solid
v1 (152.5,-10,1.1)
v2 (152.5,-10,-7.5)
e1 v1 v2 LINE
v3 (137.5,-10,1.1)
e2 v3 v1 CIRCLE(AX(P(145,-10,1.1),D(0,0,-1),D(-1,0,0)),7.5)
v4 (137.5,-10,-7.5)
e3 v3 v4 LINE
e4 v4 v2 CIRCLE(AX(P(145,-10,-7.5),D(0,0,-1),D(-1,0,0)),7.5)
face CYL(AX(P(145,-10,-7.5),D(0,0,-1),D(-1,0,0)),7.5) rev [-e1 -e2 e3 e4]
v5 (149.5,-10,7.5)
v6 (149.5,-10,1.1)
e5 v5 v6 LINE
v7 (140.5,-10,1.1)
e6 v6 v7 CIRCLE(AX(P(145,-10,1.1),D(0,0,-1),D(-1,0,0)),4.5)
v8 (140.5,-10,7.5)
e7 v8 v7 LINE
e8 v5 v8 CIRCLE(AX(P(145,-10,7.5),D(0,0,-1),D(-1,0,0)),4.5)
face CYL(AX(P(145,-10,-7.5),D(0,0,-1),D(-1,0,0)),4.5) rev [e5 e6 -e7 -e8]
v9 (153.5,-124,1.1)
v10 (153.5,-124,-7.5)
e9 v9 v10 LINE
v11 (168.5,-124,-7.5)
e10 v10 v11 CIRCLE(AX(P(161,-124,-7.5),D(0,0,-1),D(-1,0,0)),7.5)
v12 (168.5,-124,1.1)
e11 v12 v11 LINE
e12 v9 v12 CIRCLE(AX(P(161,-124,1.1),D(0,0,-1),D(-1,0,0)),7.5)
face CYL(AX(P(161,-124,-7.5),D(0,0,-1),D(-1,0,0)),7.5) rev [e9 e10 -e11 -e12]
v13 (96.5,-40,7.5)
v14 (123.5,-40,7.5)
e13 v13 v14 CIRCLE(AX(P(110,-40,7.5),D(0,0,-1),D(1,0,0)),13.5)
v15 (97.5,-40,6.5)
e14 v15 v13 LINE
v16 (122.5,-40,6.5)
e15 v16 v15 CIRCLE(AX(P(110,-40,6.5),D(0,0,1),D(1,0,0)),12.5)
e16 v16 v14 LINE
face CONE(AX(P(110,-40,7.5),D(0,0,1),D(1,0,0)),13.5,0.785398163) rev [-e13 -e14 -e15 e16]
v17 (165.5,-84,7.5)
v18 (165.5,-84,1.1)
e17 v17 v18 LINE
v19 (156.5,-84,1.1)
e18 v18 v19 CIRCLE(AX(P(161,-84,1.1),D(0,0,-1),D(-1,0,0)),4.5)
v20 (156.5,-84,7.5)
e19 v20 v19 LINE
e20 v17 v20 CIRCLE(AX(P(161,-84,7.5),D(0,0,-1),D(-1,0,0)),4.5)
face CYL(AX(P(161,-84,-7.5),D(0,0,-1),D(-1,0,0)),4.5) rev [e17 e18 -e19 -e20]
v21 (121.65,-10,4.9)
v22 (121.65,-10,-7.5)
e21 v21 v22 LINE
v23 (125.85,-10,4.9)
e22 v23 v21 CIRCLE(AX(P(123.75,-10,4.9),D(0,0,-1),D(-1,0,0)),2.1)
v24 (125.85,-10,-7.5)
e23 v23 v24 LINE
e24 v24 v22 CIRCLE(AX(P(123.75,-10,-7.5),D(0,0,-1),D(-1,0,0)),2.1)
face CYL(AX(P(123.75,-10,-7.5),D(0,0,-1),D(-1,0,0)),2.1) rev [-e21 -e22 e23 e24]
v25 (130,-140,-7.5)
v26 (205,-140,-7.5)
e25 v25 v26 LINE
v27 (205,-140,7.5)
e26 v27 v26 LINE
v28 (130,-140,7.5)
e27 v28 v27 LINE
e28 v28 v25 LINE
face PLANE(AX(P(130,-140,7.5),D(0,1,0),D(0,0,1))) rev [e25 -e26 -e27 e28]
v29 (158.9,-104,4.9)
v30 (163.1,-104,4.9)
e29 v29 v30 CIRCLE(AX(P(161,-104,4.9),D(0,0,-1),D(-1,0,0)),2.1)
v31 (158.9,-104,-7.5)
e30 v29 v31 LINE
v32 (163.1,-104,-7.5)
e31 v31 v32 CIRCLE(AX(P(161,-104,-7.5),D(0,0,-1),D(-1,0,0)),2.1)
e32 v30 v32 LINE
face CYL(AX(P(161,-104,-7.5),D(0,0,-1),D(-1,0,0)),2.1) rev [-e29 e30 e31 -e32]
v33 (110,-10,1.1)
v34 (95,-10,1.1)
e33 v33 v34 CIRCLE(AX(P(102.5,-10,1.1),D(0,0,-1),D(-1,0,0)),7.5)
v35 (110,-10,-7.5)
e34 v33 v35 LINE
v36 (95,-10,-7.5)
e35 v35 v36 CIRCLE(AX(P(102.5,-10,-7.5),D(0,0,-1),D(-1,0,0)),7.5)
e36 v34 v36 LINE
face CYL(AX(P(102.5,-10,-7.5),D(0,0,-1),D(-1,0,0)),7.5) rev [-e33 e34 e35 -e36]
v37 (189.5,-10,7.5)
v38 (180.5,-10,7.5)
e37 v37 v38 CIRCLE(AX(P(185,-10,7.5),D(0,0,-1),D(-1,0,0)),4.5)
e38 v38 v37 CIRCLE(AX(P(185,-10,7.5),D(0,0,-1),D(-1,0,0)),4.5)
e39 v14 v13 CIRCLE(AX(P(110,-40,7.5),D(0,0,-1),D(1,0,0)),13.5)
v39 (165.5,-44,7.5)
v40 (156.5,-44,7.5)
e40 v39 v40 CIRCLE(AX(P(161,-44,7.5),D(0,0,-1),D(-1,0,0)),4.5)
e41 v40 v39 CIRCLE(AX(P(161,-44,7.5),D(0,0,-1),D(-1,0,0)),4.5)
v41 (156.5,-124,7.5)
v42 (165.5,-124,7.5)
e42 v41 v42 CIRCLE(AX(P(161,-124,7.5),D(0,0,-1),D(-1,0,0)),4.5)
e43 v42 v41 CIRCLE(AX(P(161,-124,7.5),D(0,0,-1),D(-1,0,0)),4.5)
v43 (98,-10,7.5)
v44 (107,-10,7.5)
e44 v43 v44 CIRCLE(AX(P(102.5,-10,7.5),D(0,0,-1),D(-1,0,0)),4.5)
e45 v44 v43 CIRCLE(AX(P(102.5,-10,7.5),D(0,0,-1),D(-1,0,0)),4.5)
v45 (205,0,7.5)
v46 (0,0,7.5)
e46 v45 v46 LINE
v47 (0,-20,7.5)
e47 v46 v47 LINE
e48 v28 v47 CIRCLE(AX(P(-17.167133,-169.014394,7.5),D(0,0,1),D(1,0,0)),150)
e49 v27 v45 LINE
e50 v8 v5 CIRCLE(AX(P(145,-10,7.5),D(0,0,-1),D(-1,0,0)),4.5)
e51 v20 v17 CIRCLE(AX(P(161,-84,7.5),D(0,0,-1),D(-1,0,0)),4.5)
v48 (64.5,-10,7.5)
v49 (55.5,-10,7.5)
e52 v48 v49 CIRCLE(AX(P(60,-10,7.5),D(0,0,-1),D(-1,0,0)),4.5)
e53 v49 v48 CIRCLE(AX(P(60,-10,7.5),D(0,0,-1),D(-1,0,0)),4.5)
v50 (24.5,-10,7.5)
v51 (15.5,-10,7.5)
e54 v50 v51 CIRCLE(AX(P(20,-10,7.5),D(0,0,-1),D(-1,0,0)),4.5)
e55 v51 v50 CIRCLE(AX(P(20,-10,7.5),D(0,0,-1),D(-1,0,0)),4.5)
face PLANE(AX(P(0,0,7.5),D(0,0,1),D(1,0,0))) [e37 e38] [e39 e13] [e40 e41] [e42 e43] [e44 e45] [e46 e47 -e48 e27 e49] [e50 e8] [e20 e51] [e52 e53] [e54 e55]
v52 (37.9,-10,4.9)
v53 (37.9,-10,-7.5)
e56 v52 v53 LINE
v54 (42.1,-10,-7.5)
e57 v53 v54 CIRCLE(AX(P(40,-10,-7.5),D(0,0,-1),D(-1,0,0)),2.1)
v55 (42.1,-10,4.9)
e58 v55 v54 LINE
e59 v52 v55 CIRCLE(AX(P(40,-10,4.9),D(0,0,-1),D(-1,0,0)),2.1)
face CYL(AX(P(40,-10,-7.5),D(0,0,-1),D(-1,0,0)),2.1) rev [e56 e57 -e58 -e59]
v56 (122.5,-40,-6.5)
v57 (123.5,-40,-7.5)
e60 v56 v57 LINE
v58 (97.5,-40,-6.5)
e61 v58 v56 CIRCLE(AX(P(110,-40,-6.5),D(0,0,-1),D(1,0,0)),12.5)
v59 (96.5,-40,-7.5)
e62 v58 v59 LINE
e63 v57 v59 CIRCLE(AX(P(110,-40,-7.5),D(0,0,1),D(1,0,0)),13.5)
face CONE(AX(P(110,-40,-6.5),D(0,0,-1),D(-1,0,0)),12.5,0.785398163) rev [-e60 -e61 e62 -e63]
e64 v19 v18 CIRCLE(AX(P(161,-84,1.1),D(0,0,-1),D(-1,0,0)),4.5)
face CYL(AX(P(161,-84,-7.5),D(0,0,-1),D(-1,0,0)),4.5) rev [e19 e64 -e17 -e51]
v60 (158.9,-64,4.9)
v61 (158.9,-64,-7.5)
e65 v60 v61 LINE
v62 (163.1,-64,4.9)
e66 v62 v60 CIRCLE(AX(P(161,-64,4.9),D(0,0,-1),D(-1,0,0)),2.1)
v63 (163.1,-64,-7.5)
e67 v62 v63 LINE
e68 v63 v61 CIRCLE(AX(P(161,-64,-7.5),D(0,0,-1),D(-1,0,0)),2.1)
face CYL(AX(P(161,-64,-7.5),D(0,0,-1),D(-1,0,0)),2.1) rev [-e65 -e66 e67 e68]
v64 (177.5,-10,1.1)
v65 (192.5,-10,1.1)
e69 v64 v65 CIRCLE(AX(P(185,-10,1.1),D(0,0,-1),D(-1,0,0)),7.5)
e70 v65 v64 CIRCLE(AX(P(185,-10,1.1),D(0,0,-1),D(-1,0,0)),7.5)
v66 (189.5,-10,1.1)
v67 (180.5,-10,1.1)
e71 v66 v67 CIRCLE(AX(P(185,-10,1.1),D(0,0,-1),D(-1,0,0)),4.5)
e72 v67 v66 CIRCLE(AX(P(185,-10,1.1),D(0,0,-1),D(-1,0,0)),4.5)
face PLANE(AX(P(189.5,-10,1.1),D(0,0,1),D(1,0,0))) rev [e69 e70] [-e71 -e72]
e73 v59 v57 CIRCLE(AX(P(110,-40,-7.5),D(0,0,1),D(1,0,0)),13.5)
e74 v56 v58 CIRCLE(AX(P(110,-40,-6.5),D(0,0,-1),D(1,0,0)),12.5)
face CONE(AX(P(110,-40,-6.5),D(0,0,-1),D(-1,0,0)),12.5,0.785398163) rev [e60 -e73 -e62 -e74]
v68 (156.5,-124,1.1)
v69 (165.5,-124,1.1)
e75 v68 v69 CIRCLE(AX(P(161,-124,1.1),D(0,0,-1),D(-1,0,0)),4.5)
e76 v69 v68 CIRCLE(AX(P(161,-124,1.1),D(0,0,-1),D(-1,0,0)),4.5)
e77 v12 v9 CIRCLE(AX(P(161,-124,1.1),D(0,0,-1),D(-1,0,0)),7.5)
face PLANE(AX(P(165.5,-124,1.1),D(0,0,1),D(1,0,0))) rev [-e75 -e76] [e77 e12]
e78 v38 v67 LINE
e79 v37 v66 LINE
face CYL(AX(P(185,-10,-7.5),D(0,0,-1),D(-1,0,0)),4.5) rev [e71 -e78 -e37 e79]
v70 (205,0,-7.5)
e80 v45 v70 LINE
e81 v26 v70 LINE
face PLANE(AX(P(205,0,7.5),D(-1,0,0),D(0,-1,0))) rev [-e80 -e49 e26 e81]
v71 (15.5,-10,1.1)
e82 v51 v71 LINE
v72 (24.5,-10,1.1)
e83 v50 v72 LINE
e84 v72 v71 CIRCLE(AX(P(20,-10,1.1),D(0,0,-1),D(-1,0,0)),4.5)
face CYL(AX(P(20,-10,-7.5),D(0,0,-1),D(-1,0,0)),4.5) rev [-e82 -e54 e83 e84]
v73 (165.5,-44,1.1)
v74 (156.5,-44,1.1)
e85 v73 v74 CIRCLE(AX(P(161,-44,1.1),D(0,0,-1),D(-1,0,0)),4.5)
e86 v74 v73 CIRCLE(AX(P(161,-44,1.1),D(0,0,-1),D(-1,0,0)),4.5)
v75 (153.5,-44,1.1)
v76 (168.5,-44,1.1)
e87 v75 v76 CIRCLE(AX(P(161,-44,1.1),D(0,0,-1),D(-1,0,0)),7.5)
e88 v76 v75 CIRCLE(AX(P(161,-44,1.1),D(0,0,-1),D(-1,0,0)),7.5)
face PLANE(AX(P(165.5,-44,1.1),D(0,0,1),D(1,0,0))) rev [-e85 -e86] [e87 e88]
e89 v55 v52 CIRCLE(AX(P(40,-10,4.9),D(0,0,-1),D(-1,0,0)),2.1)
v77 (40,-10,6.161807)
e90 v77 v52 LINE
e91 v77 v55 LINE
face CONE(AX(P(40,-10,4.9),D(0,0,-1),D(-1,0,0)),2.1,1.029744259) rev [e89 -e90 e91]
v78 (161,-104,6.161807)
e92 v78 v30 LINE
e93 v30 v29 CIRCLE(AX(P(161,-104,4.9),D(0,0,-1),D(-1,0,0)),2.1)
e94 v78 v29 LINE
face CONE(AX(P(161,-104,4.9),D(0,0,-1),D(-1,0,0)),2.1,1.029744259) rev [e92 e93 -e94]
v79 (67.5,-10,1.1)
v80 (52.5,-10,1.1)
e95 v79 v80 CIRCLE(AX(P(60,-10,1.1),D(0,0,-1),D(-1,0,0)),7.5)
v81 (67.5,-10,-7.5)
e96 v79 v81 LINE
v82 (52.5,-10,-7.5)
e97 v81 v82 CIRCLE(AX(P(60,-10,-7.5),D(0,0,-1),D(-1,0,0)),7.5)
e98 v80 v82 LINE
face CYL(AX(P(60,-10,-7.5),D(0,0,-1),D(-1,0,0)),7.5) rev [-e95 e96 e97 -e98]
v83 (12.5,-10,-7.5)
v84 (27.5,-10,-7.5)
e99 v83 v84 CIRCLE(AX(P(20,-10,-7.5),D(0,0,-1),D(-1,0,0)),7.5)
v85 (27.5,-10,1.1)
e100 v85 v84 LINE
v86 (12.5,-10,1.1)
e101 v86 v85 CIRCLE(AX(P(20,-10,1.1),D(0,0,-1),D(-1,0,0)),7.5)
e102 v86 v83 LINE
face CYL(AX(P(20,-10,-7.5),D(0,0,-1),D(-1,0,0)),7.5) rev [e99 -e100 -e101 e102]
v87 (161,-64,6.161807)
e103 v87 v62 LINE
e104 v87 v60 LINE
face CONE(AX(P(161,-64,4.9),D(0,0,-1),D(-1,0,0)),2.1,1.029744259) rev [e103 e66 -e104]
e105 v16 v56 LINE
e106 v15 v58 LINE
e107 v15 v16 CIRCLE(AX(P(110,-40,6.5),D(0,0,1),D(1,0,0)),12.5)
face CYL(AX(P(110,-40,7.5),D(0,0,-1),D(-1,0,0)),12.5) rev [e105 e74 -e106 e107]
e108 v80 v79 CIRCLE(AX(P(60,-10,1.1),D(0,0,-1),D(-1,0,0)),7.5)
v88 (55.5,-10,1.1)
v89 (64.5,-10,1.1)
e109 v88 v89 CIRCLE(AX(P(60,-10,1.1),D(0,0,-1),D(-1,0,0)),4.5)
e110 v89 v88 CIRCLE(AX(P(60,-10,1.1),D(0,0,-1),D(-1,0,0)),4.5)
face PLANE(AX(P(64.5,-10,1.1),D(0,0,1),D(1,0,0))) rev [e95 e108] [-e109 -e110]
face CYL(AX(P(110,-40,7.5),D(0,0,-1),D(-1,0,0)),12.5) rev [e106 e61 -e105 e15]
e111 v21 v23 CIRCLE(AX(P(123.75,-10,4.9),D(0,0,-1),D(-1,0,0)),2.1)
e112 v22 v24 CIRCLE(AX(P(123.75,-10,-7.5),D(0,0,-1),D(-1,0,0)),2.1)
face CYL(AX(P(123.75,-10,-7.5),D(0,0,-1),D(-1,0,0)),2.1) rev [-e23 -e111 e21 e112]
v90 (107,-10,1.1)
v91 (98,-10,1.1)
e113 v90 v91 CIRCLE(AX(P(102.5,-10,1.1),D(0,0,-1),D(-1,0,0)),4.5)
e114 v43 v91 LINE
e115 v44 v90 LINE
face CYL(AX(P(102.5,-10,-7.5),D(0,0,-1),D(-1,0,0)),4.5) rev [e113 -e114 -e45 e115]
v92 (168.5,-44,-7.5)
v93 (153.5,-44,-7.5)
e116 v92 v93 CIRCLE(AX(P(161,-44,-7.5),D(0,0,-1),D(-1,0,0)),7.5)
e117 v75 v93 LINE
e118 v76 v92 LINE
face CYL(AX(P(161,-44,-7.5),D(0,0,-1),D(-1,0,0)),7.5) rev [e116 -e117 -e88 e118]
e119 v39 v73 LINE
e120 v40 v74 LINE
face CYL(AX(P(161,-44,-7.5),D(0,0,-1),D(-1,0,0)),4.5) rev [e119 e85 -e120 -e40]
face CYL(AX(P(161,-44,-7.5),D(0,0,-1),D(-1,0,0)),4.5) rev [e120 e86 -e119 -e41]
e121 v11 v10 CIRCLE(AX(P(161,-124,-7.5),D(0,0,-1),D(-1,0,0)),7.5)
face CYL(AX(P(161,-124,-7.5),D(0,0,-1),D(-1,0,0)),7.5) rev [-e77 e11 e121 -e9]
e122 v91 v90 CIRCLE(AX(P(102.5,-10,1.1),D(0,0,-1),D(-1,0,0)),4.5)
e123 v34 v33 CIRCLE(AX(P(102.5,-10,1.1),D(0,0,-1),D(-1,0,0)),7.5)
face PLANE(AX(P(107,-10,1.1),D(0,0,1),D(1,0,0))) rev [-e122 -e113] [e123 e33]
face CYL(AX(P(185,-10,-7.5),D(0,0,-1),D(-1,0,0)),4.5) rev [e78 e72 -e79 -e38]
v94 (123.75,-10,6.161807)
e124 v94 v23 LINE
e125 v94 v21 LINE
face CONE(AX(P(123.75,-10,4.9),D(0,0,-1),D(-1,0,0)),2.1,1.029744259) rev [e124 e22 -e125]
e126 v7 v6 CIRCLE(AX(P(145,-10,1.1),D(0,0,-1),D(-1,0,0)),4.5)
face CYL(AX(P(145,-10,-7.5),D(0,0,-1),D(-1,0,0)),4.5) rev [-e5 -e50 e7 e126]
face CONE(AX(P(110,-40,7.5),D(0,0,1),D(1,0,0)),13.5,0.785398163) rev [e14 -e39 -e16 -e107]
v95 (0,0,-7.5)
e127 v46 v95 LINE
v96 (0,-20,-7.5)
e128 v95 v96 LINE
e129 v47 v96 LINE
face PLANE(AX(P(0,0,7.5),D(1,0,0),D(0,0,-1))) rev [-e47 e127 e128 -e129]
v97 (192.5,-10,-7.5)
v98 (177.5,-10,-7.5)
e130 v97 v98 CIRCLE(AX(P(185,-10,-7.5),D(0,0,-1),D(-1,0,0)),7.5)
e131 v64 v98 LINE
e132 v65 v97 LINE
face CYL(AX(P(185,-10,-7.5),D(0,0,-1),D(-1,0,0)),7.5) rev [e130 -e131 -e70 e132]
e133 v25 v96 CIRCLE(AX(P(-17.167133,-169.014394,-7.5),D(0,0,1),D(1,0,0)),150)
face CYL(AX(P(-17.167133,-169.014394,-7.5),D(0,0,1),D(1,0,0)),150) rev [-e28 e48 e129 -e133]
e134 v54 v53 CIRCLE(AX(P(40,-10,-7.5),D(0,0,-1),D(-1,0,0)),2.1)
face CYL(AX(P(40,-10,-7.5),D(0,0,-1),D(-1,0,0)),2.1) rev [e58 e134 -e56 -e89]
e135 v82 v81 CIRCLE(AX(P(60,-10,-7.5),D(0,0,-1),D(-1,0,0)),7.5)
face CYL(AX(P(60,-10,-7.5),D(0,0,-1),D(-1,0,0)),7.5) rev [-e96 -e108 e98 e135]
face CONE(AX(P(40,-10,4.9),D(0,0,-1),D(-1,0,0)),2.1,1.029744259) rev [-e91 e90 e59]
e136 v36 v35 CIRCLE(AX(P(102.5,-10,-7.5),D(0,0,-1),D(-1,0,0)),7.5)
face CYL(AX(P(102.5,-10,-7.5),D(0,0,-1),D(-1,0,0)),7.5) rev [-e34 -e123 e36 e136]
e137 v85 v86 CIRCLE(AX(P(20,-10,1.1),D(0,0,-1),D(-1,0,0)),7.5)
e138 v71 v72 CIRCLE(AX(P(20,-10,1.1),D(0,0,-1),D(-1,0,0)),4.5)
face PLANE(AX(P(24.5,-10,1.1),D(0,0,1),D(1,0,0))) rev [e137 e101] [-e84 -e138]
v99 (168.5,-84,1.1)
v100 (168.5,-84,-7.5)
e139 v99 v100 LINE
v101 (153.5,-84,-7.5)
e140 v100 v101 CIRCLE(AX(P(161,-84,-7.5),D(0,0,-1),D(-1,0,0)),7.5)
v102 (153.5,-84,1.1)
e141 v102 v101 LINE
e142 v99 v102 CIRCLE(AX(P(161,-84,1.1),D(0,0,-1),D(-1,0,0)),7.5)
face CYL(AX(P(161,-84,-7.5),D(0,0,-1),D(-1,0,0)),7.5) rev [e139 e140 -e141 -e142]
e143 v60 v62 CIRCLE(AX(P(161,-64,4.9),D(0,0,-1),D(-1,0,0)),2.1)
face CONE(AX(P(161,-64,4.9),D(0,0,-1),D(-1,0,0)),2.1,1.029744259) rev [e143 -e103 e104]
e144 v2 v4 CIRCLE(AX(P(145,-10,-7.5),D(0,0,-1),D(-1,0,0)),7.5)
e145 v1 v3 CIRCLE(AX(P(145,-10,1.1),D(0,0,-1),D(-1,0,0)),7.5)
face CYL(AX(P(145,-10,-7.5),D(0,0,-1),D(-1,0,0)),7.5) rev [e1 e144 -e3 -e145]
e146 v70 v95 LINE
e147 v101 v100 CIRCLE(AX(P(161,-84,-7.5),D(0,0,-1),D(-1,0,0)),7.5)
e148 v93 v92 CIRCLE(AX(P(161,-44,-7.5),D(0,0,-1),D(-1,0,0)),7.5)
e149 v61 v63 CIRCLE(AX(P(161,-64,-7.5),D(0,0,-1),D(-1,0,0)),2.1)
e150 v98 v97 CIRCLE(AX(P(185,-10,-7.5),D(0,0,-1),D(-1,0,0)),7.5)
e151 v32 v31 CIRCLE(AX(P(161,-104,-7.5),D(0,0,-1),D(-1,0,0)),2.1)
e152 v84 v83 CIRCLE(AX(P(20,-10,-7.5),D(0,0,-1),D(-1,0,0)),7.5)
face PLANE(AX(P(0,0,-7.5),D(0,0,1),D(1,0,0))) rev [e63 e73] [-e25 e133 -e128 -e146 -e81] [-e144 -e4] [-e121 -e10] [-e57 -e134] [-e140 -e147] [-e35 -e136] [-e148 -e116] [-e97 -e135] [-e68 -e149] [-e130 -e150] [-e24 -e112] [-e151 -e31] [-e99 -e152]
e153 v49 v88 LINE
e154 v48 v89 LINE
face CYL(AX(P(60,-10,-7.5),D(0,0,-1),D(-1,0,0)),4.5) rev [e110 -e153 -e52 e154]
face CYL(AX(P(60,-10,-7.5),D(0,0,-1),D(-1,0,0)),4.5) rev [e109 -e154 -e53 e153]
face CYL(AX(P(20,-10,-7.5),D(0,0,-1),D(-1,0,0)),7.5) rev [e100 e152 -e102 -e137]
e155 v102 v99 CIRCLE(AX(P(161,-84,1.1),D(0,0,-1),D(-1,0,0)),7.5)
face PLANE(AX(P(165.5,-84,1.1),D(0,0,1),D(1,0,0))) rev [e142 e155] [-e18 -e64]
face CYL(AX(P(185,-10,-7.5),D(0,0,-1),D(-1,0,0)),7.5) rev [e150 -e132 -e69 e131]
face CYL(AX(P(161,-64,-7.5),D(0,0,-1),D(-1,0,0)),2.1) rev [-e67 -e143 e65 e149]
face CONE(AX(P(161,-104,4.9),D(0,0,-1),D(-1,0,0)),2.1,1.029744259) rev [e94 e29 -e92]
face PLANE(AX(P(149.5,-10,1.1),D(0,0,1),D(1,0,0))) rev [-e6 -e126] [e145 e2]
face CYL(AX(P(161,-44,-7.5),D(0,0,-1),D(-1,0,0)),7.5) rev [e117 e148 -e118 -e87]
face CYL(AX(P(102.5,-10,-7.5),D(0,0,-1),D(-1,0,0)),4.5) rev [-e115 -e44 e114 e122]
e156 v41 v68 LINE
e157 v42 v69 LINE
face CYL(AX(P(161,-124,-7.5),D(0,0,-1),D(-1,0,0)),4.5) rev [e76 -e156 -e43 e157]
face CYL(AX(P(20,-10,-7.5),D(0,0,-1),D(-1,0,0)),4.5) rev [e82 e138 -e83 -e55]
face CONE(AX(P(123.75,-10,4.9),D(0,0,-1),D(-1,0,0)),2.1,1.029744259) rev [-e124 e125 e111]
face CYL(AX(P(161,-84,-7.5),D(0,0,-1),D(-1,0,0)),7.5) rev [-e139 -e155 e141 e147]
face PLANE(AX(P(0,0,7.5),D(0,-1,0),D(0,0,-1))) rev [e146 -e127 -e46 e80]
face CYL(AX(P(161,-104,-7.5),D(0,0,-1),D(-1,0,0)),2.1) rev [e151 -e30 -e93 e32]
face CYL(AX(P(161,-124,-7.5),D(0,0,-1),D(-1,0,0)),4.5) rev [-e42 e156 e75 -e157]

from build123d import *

# Parameters (mm, degrees)
EXTRUDE_1_DEPTH              = 7.5
HOLE_WIZARD_M8_2_D           = 9
HOLE_WIZARD_M8_2_CBORE_D     = 15
HOLE_WIZARD_M8_2_CBORE_DEPTH = 8.6
HOLE_WIZARD_M5_1_D           = 4.2
HOLE_WIZARD_M5_1_DEPTH       = 12.4
HOLE_WIZARD_M5_1_TIP         = 1.2618073
SKETCH_11_R                  = 150
CUT_EXTRUDE_4_DEPTH          = 249.696602309
SKETCH_12_R                  = 12.5
CUT_EXTRUDE_5_DEPTH          = 249.696602309
CHAMFER_1_SIZE               = 1


with BuildPart() as part:
    # 草图1 → 凸台-拉伸1 (new, symmetric)
    with BuildSketch(Plane.XY):
        Polygon((0, 0), (205, 0), (205, -140), (130, -140), (0, -20), align=None)
    extrude(amount=EXTRUDE_1_DEPTH, both=True)

    # M8 六角凹头螺钉的柱形沉头孔2 (through all)
    with Locations(Plane(origin=(0, 0, -7.5), x_dir=(1, 0, 0), z_dir=(0, 0, -1))):
        with Locations((20, 10), (60, 10), (102.5, 10), (145, 10), (161, 44), (161, 84), (161, 124), (185, 10)):
            CounterBoreHole(HOLE_WIZARD_M8_2_D / 2, HOLE_WIZARD_M8_2_CBORE_D / 2, HOLE_WIZARD_M8_2_CBORE_DEPTH)

    # M5 螺纹孔1
    with Locations(Plane(origin=(0, 0, -7.5), x_dir=(1, 0, 0), z_dir=(0, 0, -1))):
        with Locations((40, 10), (123.75, 10), (161, 64), (161, 104)):
            Hole(HOLE_WIZARD_M5_1_D / 2, depth=HOLE_WIZARD_M5_1_DEPTH)
            with Locations((0, 0, -(HOLE_WIZARD_M5_1_DEPTH + HOLE_WIZARD_M5_1_TIP / 2))):  # 118° drill point
                Cone(0, HOLE_WIZARD_M5_1_D / 2, HOLE_WIZARD_M5_1_TIP, mode=Mode.SUBTRACT)

    # 草图11 → 切除-拉伸4 (cut, through all)
    with BuildSketch(Plane.XY.offset(7.5)):
        with Locations((-17.167132722, -169.014393782)):
            Circle(SKETCH_11_R)
    extrude(amount=-CUT_EXTRUDE_4_DEPTH, mode=Mode.SUBTRACT)

    # 草图12 → 切除-拉伸5 (cut, through all)
    with BuildSketch(Plane(origin=(0, 0, -7.5), x_dir=(-1, 0, 0), z_dir=(0, 0, -1))):
        with Locations((-110, -40)):
            Circle(SKETCH_12_R)
    extrude(amount=-CUT_EXTRUDE_5_DEPTH, mode=Mode.SUBTRACT)

    # 倒角1
    chamfer_1_edges = [part.edges().sort_by_distance(p)[0] for p in [
        (122.5, -40, 7.5),
        (122.5, -40, -7.5),
    ]]
    chamfer(chamfer_1_edges, length=CHAMFER_1_SIZE)


solid = part.part
